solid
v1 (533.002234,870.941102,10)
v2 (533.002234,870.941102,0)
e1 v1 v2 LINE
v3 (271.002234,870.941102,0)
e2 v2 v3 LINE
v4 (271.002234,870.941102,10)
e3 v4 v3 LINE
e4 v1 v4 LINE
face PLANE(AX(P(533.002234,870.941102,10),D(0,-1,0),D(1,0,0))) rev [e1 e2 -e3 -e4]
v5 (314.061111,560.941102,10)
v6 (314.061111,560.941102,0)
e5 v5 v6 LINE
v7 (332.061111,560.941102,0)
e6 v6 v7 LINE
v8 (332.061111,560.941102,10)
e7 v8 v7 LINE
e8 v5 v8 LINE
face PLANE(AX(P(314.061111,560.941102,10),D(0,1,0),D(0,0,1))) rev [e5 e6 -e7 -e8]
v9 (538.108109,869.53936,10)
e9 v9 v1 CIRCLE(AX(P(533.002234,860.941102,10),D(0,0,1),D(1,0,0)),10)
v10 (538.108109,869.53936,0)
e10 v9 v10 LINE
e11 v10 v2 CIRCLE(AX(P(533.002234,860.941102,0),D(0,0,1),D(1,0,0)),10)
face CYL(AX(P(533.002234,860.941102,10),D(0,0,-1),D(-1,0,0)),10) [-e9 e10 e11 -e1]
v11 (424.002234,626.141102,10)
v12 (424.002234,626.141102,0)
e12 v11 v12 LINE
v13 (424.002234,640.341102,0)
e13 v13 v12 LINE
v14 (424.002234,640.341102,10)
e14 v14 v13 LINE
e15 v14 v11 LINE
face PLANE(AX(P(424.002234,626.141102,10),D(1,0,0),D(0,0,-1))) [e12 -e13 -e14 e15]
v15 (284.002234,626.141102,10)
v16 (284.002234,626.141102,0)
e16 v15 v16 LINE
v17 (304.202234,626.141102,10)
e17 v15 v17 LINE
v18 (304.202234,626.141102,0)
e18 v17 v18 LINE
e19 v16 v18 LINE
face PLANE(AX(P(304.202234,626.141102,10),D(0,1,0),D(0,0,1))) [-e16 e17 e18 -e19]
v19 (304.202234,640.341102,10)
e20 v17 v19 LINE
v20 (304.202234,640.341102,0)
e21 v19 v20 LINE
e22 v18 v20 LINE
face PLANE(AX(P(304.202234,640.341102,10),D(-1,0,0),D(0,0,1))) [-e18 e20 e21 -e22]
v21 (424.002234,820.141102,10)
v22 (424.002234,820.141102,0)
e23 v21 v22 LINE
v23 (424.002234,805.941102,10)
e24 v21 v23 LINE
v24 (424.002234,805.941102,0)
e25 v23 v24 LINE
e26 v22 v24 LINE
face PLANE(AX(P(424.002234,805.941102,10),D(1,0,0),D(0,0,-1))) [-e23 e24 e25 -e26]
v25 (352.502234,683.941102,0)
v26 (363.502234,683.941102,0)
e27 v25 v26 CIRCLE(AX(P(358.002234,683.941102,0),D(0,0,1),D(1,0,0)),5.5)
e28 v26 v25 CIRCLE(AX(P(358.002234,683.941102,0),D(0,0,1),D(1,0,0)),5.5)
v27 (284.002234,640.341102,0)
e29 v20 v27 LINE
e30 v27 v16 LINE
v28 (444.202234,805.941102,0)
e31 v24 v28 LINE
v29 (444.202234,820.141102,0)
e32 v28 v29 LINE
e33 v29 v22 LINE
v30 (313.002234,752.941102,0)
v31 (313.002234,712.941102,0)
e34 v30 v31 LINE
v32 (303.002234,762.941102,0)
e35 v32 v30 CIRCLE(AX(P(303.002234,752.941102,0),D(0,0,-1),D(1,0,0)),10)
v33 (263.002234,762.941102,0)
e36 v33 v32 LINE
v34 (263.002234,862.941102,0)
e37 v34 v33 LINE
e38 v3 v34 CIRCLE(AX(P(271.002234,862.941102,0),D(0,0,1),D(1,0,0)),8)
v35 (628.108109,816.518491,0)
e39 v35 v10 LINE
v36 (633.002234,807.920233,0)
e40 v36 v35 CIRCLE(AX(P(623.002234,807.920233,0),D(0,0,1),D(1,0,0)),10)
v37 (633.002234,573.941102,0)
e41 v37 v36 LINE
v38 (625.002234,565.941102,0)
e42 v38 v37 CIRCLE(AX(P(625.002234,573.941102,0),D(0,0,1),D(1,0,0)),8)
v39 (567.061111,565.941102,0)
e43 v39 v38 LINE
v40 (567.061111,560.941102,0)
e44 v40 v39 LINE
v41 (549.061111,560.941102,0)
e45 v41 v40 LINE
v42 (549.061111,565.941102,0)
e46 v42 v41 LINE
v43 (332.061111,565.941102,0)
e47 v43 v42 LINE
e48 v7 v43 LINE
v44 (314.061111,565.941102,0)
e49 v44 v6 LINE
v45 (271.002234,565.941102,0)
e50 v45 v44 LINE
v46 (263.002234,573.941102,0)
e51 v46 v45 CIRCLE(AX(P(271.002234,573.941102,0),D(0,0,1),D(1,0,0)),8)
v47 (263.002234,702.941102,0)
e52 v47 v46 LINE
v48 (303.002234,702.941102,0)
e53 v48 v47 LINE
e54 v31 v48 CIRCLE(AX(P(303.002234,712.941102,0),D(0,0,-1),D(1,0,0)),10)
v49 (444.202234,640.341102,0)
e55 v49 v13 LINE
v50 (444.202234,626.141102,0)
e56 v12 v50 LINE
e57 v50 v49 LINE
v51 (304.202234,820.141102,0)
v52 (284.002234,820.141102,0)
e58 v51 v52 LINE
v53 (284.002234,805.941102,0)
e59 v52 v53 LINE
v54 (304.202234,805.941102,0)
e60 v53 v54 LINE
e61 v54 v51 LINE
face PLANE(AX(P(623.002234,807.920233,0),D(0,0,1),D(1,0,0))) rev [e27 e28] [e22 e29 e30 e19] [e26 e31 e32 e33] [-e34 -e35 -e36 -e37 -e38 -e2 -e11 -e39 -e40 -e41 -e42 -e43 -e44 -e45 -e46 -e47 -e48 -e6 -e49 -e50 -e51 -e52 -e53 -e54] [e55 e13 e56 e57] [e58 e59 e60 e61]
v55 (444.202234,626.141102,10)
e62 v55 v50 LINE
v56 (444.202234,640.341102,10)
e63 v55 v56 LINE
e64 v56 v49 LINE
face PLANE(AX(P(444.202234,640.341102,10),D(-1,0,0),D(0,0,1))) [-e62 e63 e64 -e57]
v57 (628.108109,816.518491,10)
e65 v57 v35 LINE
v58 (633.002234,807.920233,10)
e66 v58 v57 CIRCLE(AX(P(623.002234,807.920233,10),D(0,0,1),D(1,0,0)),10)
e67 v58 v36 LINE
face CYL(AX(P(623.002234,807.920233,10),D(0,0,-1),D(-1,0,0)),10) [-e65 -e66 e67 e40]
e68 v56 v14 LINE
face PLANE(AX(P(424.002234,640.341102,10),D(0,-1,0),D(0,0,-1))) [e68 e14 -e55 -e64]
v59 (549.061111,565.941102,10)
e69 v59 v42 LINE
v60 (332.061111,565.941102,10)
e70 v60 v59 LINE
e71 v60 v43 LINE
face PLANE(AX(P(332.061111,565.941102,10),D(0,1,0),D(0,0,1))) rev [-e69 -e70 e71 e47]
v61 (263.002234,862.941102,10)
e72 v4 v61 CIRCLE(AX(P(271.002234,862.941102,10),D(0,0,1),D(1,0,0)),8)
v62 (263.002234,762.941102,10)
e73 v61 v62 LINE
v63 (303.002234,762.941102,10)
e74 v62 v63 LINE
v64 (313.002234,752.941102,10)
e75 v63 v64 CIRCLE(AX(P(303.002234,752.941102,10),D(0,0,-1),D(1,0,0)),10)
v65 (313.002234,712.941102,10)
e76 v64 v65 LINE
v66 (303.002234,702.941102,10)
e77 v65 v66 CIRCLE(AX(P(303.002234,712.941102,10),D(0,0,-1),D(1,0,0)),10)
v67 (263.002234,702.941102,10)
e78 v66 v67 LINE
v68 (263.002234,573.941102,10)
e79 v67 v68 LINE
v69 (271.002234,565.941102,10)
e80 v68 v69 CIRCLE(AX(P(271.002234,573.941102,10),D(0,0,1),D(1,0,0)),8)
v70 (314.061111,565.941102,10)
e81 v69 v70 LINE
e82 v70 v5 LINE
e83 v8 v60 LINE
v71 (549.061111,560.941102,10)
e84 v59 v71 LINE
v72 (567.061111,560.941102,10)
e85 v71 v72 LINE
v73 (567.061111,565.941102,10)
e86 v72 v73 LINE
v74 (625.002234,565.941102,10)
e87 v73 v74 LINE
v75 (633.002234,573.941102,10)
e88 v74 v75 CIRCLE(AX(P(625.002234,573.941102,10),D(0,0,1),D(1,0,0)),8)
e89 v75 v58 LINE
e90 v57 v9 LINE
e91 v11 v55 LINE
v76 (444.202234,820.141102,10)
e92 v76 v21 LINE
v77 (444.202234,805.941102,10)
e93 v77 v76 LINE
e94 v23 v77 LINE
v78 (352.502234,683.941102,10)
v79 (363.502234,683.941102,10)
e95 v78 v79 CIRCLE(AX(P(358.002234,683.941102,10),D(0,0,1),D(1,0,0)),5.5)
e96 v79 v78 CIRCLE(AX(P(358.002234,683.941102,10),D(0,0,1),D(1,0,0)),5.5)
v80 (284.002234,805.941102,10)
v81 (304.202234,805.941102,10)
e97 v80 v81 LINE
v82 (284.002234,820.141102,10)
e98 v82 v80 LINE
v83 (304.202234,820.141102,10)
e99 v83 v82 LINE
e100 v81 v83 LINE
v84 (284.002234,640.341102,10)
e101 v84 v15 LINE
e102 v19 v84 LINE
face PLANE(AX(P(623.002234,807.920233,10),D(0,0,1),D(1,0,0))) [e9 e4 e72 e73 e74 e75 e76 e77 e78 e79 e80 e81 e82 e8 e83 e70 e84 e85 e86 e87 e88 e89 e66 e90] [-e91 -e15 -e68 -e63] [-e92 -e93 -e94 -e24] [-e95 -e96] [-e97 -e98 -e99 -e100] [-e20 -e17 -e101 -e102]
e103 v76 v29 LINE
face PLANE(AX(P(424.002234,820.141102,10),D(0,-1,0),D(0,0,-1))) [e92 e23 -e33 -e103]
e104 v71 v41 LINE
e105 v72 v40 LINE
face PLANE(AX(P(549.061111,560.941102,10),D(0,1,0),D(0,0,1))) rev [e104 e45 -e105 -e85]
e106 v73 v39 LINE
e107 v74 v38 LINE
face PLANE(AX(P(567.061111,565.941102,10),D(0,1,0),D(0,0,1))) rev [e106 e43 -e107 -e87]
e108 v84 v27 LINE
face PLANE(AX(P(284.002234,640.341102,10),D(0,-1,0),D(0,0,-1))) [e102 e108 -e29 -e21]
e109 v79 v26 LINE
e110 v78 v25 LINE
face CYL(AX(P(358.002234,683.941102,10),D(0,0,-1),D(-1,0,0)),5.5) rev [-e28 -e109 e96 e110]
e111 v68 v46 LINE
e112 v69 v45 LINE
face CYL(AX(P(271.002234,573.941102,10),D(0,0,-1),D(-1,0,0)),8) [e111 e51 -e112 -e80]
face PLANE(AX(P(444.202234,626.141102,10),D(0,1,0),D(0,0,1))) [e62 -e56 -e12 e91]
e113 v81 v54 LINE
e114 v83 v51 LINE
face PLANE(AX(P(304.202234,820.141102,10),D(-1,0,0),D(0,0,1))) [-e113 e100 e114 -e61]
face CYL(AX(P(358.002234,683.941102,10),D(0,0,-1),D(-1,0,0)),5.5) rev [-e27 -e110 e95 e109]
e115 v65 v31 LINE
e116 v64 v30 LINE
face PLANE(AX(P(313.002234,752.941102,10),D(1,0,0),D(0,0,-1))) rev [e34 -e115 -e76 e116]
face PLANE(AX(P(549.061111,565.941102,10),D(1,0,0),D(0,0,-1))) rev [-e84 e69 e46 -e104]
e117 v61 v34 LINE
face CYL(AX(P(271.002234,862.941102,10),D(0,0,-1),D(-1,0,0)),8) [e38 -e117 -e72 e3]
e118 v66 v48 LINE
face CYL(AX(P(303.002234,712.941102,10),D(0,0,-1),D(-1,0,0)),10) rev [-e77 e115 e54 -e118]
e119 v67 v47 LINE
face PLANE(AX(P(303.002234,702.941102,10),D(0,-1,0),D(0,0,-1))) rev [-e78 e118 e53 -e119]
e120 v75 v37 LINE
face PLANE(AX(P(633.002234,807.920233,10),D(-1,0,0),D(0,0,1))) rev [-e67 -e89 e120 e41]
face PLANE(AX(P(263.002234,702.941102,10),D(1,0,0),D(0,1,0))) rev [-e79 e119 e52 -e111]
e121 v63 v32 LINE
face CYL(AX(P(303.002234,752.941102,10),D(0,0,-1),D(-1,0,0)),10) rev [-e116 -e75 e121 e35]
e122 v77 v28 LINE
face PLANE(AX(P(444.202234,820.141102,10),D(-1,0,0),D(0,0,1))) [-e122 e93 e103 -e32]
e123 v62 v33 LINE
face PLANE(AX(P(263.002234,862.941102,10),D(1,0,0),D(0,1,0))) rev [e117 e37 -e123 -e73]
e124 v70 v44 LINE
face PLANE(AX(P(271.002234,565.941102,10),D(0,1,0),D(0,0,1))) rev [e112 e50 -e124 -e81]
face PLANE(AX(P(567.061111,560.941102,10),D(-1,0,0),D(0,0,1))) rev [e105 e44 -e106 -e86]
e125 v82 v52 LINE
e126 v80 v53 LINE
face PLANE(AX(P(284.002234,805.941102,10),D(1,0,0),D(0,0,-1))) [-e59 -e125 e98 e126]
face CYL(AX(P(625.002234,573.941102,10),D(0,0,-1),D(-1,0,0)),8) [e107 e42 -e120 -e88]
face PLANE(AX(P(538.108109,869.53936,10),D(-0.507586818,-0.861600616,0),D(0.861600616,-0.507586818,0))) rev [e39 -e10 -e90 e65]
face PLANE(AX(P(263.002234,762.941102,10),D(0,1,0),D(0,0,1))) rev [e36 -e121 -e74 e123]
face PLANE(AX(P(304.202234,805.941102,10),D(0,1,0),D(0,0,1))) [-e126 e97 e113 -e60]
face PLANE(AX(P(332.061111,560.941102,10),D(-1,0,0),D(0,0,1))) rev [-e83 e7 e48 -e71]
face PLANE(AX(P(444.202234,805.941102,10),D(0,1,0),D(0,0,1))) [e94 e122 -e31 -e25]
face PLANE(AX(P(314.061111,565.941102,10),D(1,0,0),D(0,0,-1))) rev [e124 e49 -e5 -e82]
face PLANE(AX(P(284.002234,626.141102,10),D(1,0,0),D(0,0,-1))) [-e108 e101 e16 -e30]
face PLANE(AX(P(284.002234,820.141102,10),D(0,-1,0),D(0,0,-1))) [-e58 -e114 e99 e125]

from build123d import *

# Parameters (mm, degrees)
SKETCH1_R           = 5.5
SKETCH1_W           = 20.2
SKETCH1_H           = 14.2
BOSS_EXTRUDE1_DEPTH = 10


with BuildPart() as part:
    # Sketch1 → Boss-Extrude1 (new body)
    with BuildSketch(Plane.XY):
        with BuildLine():
            Line((538.108108788, 869.539360157), (628.108108788, 816.518490855))
            ThreePointArc((628.108108788, 816.518490855), (631.692997782, 812.867012092), (633.002234094, 807.920232682))
            Line((633.002234094, 807.920232682), (633.002234094, 573.941101984))
            ThreePointArc((633.002234094, 573.941101984), (630.659088344, 568.284247734), (625.002234094, 565.941101984))
            Line((625.002234094, 565.941101984), (567.061111031, 565.941101984))
            Line((567.061111031, 565.941101984), (567.061111031, 560.941101984))
            Line((567.061111031, 560.941101984), (549.061111031, 560.941101984))
            Line((549.061111031, 560.941101984), (549.061111031, 565.941101984))
            Line((549.061111031, 565.941101984), (332.061111031, 565.941101984))
            Line((332.061111031, 565.941101984), (332.061111031, 560.941101984))
            Line((332.061111031, 560.941101984), (314.061111031, 560.941101984))
            Line((314.061111031, 560.941101984), (314.061111031, 565.941101984))
            Line((314.061111031, 565.941101984), (271.002234094, 565.941101984))
            ThreePointArc((271.002234094, 565.941101984), (265.345379845, 568.284247734), (263.002234094, 573.941101984))
            Line((263.002234094, 573.941101984), (263.002234094, 702.941101984))
            Line((263.002234094, 702.941101984), (303.002234094, 702.941101984))
            ThreePointArc((303.002234094, 702.941101984), (310.073301906, 705.870034172), (313.002234094, 712.941101984))
            Line((313.002234094, 712.941101984), (313.002234094, 752.941101984))
            ThreePointArc((313.002234094, 752.941101984), (310.073301906, 760.012169796), (303.002234094, 762.941101984))
            Line((303.002234094, 762.941101984), (263.002234094, 762.941101984))
            Line((263.002234094, 762.941101984), (263.002234094, 862.941101984))
            ThreePointArc((263.002234094, 862.941101984), (265.345379845, 868.597956233), (271.002234094, 870.941101984))
            Line((271.002234094, 870.941101984), (533.002234094, 870.941101984))
            ThreePointArc((533.002234094, 870.941101984), (535.649630765, 870.584301187), (538.108108788, 869.539360157))
        make_face()
        with Locations((358.002234094, 683.941101984)):
            Circle(SKETCH1_R, mode=Mode.SUBTRACT)
        with Locations((294.102234094, 633.241101984)):
            Rectangle(SKETCH1_W, SKETCH1_H, mode=Mode.SUBTRACT)
        with Locations((434.102234094, 633.241101984)):
            Rectangle(SKETCH1_W, SKETCH1_H, mode=Mode.SUBTRACT)
        with Locations((294.102234094, 813.041101984)):
            Rectangle(SKETCH1_W, SKETCH1_H, mode=Mode.SUBTRACT)
        with Locations((434.102234094, 813.041101984)):
            Rectangle(SKETCH1_W, SKETCH1_H, mode=Mode.SUBTRACT)
    extrude(amount=BOSS_EXTRUDE1_DEPTH)


solid = part.part
